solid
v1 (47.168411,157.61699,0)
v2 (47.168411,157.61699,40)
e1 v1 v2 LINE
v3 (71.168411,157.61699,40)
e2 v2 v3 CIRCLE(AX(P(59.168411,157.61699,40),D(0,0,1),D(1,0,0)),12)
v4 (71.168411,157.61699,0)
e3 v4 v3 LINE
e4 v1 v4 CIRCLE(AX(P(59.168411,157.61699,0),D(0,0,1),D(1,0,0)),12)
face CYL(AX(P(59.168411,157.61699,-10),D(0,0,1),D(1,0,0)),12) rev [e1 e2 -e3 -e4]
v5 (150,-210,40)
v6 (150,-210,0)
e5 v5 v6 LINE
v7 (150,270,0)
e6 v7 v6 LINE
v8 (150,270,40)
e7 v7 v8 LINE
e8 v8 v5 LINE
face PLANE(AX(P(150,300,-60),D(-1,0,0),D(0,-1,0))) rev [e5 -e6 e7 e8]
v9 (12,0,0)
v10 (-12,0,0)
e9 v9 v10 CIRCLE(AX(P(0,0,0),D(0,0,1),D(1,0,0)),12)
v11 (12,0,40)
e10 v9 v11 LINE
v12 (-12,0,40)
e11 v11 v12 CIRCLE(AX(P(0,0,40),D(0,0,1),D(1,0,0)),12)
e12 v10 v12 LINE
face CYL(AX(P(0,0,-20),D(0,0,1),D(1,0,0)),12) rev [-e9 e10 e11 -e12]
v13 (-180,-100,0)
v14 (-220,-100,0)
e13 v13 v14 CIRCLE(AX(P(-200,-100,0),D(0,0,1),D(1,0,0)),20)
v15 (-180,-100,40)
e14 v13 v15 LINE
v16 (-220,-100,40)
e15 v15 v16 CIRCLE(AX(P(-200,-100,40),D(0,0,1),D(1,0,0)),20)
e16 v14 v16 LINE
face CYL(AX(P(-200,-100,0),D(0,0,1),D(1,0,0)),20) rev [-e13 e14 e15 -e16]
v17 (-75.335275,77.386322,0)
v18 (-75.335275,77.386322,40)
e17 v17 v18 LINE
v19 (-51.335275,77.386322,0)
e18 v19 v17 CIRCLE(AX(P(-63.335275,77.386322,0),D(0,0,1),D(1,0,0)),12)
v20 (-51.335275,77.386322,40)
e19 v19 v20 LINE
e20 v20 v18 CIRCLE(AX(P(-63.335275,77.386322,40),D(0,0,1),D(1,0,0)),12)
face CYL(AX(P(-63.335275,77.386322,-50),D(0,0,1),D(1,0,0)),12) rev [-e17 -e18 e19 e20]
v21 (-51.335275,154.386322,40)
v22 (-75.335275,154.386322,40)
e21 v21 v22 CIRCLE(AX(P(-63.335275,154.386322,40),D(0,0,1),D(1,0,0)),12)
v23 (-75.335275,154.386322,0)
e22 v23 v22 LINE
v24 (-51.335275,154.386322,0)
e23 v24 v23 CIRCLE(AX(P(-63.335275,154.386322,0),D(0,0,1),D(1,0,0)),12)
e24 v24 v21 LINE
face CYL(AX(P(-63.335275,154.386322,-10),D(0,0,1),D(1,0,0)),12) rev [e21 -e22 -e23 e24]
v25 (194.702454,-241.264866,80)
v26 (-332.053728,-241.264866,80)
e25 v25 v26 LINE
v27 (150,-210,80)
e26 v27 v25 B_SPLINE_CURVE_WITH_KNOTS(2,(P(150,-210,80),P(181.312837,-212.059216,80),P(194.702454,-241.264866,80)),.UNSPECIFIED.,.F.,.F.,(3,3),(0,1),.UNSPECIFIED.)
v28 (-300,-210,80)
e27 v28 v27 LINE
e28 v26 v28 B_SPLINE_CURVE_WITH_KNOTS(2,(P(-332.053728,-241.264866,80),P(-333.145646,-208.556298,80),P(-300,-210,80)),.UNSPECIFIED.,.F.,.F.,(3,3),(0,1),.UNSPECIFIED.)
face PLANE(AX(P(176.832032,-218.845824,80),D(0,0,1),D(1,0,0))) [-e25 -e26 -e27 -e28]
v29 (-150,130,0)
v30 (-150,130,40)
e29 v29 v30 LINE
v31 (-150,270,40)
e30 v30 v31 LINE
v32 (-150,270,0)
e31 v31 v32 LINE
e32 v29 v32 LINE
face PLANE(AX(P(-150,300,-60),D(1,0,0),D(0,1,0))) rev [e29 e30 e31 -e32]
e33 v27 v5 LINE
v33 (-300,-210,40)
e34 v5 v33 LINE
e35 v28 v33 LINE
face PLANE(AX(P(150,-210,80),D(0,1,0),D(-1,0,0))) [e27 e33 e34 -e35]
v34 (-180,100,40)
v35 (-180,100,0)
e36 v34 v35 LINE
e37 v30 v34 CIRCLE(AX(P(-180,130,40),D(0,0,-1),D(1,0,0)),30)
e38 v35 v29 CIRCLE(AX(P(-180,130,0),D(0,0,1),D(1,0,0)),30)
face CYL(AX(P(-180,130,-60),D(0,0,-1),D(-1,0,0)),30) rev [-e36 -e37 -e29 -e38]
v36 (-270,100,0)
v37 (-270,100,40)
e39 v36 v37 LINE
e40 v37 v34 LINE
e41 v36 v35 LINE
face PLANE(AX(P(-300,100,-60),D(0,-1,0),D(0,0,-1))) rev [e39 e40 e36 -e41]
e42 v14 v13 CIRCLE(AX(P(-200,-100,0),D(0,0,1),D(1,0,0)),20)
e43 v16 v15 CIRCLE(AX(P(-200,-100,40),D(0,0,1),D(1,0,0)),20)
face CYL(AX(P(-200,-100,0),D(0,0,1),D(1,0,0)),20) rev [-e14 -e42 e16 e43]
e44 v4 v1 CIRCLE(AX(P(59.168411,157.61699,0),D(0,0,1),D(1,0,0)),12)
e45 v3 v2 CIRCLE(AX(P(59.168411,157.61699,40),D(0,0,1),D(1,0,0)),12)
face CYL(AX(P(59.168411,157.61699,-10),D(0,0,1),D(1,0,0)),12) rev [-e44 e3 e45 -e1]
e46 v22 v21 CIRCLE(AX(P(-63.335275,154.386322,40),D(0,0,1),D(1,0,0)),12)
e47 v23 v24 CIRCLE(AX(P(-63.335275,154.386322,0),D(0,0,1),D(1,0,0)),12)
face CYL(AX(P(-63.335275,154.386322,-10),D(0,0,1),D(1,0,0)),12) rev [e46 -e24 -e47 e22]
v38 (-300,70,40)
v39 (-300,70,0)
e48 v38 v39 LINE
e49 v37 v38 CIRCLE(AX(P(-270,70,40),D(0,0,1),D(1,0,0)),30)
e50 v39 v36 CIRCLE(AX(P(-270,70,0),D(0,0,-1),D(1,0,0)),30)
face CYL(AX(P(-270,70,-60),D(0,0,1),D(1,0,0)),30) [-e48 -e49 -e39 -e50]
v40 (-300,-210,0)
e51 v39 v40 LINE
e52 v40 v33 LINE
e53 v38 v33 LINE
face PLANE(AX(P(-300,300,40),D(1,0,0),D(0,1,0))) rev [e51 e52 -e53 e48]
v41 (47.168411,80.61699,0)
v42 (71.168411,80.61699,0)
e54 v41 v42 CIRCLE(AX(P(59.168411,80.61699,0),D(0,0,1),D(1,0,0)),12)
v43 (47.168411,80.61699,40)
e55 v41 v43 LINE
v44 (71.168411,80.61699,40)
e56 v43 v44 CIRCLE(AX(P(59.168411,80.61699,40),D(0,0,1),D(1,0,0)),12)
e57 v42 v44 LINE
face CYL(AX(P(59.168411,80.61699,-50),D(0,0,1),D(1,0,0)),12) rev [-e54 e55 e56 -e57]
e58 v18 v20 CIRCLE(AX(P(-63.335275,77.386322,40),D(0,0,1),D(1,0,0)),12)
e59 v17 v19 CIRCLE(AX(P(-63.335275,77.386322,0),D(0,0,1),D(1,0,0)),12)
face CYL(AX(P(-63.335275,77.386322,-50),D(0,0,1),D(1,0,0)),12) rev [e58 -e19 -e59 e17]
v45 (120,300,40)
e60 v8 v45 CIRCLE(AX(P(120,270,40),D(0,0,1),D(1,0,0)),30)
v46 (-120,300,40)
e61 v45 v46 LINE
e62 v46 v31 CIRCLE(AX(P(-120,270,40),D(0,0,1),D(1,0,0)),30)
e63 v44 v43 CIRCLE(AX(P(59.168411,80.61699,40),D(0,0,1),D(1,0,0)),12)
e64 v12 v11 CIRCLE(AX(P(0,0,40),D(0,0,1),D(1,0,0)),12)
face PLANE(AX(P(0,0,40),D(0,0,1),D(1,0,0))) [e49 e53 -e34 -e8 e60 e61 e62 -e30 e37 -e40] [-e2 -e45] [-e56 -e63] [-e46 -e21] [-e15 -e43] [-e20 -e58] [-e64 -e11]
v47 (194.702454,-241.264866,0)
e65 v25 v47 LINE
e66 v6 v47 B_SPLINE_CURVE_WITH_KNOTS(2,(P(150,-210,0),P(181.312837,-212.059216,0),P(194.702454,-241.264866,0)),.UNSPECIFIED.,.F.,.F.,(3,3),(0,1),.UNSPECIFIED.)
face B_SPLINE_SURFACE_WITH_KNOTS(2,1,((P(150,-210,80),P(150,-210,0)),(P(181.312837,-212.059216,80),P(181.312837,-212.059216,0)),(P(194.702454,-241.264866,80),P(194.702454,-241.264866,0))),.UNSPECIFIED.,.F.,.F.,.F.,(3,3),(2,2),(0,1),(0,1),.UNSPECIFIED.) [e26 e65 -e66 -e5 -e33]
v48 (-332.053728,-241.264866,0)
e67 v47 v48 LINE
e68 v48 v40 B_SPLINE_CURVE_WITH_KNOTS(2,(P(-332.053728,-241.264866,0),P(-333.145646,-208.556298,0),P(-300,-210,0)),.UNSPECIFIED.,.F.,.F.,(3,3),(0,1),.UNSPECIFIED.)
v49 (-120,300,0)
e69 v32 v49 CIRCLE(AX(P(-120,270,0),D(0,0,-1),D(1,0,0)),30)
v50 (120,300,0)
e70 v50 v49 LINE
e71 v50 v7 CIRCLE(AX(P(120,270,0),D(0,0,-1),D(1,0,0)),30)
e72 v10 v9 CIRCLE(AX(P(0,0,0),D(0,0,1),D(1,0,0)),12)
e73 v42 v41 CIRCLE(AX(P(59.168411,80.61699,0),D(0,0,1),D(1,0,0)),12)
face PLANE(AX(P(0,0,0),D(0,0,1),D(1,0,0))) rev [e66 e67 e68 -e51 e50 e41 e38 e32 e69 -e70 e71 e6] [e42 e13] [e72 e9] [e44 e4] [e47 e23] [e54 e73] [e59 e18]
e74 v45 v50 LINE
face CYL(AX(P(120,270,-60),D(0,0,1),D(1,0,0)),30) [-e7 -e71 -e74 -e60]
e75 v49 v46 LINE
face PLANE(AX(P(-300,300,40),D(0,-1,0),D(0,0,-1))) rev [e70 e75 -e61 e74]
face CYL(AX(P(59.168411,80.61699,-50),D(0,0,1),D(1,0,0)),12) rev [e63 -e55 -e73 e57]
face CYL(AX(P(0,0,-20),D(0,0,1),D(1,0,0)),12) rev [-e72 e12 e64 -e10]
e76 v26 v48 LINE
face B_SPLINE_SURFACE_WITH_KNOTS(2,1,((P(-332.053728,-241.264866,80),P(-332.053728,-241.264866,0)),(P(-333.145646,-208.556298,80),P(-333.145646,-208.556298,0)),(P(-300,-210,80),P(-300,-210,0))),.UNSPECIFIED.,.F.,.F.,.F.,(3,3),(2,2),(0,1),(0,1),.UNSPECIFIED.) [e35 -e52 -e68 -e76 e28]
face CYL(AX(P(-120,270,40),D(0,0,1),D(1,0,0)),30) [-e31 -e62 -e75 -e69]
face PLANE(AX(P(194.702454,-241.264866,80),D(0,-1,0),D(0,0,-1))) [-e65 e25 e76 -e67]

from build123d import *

# Parameters (mm, degrees)
SKETCH1_W           = 600
SKETCH1_H           = 600
BOSS_EXTRUDE1_DEPTH = 40
SKETCH2_R           = 20
CUT_EXTRUDE1_DEPTH  = 40
SKETCH3_R           = 12
CUT_EXTRUDE2_DEPTH  = 60
SKETCH4_R           = 12
CUT_EXTRUDE3_DEPTH  = 90
SKETCH5_W           = 150
SKETCH5_H           = 600
CUT_EXTRUDE4_DEPTH  = 100
SKETCH6_W           = 150
SKETCH6_H           = 200
CUT_EXTRUDE5_DEPTH  = 100
SKETCH7_W           = 450
SKETCH7_H           = 90
CUT_EXTRUDE6_DEPTH  = 100
SKETCH9_R           = 12
CUT_EXTRUDE7_DEPTH  = 50
FILLET1_R           = 30
BOSS_EXTRUDE2_DEPTH = 80


with BuildPart() as part:
    # Sketch1 → Boss-Extrude1 (new body)
    with BuildSketch(Plane.XY):
        Rectangle(SKETCH1_W, SKETCH1_H)
    extrude(amount=BOSS_EXTRUDE1_DEPTH)

    # Sketch2 → Cut-Extrude1 (cut)
    with BuildSketch(Plane.XY.offset(40)):
        with Locations((-200, -100)):
            Circle(SKETCH2_R)
    extrude(amount=-CUT_EXTRUDE1_DEPTH, mode=Mode.SUBTRACT)

    # Sketch3 → Cut-Extrude2 (cut)
    with BuildSketch(Plane.XY.offset(40)):
        Circle(SKETCH3_R)
    extrude(amount=-CUT_EXTRUDE2_DEPTH, mode=Mode.SUBTRACT)

    # Sketch4 → Cut-Extrude3 (cut)
    with BuildSketch(Plane.XY.offset(40)):
        with Locations((-63.335275248, 77.386322495)):
            Circle(SKETCH4_R)
        with Locations((59.168411159, 80.616990275)):
            Circle(SKETCH4_R)
    extrude(amount=-CUT_EXTRUDE3_DEPTH, mode=Mode.SUBTRACT)

    # Sketch5 → Cut-Extrude4 (cut)
    with BuildSketch(Plane.XY.offset(40)):
        with Locations((225, 0)):
            Rectangle(SKETCH5_W, SKETCH5_H)
    extrude(amount=-CUT_EXTRUDE4_DEPTH, mode=Mode.SUBTRACT)

    # Sketch6 → Cut-Extrude5 (cut)
    with BuildSketch(Plane.XY.offset(40)):
        with Locations((-225, 200)):
            Rectangle(SKETCH6_W, SKETCH6_H)
    extrude(amount=-CUT_EXTRUDE5_DEPTH, mode=Mode.SUBTRACT)

    # Sketch7 → Cut-Extrude6 (cut)
    with BuildSketch(Plane.XY.offset(40)):
        with Locations((-75, -255)):
            Rectangle(SKETCH7_W, SKETCH7_H)
    extrude(amount=-CUT_EXTRUDE6_DEPTH, mode=Mode.SUBTRACT)

    # Sketch9 → Cut-Extrude7 (cut)
    with BuildSketch(Plane.XY.offset(40)):
        with Locations((-63.335275248, 154.386322495)):
            Circle(SKETCH9_R)
        with Locations((59.168411159, 157.616990275)):
            Circle(SKETCH9_R)
    extrude(amount=-CUT_EXTRUDE7_DEPTH, mode=Mode.SUBTRACT)

    # Fillet1
    fillet1_edges = [part.edges().sort_by_distance(p)[0] for p in [
        (150, 300, 20),
        (-300, 100, 20),
        (-150, 300, 20),
        (-150, 100, 20),
    ]]
    fillet(fillet1_edges, radius=FILLET1_R)

    # Sketch10 → Boss-Extrude2 (add)
    with BuildSketch(Plane(origin=(0, 0, 0), x_dir=(-1, 0, 0), z_dir=(0, 0, -1))):
        with BuildLine():
            Line((-150, -210), (300, -210))
            add(Edge.make_bspline(
                [(300, -210), (333.145645994, -208.556298113), (332.053728057, -241.264865933)],
                knots=[0, 0, 0, 1, 1, 1], degree=2))
            Line((332.053728057, -241.264865933), (-194.702453995, -241.264865933))
            add(Edge.make_bspline(
                [(-150, -210), (-181.312836573, -212.059215881), (-194.702453995, -241.264865933)],
                knots=[0, 0, 0, 1, 1, 1], degree=2))
        make_face()
    extrude(amount=-BOSS_EXTRUDE2_DEPTH)


solid = part.part
